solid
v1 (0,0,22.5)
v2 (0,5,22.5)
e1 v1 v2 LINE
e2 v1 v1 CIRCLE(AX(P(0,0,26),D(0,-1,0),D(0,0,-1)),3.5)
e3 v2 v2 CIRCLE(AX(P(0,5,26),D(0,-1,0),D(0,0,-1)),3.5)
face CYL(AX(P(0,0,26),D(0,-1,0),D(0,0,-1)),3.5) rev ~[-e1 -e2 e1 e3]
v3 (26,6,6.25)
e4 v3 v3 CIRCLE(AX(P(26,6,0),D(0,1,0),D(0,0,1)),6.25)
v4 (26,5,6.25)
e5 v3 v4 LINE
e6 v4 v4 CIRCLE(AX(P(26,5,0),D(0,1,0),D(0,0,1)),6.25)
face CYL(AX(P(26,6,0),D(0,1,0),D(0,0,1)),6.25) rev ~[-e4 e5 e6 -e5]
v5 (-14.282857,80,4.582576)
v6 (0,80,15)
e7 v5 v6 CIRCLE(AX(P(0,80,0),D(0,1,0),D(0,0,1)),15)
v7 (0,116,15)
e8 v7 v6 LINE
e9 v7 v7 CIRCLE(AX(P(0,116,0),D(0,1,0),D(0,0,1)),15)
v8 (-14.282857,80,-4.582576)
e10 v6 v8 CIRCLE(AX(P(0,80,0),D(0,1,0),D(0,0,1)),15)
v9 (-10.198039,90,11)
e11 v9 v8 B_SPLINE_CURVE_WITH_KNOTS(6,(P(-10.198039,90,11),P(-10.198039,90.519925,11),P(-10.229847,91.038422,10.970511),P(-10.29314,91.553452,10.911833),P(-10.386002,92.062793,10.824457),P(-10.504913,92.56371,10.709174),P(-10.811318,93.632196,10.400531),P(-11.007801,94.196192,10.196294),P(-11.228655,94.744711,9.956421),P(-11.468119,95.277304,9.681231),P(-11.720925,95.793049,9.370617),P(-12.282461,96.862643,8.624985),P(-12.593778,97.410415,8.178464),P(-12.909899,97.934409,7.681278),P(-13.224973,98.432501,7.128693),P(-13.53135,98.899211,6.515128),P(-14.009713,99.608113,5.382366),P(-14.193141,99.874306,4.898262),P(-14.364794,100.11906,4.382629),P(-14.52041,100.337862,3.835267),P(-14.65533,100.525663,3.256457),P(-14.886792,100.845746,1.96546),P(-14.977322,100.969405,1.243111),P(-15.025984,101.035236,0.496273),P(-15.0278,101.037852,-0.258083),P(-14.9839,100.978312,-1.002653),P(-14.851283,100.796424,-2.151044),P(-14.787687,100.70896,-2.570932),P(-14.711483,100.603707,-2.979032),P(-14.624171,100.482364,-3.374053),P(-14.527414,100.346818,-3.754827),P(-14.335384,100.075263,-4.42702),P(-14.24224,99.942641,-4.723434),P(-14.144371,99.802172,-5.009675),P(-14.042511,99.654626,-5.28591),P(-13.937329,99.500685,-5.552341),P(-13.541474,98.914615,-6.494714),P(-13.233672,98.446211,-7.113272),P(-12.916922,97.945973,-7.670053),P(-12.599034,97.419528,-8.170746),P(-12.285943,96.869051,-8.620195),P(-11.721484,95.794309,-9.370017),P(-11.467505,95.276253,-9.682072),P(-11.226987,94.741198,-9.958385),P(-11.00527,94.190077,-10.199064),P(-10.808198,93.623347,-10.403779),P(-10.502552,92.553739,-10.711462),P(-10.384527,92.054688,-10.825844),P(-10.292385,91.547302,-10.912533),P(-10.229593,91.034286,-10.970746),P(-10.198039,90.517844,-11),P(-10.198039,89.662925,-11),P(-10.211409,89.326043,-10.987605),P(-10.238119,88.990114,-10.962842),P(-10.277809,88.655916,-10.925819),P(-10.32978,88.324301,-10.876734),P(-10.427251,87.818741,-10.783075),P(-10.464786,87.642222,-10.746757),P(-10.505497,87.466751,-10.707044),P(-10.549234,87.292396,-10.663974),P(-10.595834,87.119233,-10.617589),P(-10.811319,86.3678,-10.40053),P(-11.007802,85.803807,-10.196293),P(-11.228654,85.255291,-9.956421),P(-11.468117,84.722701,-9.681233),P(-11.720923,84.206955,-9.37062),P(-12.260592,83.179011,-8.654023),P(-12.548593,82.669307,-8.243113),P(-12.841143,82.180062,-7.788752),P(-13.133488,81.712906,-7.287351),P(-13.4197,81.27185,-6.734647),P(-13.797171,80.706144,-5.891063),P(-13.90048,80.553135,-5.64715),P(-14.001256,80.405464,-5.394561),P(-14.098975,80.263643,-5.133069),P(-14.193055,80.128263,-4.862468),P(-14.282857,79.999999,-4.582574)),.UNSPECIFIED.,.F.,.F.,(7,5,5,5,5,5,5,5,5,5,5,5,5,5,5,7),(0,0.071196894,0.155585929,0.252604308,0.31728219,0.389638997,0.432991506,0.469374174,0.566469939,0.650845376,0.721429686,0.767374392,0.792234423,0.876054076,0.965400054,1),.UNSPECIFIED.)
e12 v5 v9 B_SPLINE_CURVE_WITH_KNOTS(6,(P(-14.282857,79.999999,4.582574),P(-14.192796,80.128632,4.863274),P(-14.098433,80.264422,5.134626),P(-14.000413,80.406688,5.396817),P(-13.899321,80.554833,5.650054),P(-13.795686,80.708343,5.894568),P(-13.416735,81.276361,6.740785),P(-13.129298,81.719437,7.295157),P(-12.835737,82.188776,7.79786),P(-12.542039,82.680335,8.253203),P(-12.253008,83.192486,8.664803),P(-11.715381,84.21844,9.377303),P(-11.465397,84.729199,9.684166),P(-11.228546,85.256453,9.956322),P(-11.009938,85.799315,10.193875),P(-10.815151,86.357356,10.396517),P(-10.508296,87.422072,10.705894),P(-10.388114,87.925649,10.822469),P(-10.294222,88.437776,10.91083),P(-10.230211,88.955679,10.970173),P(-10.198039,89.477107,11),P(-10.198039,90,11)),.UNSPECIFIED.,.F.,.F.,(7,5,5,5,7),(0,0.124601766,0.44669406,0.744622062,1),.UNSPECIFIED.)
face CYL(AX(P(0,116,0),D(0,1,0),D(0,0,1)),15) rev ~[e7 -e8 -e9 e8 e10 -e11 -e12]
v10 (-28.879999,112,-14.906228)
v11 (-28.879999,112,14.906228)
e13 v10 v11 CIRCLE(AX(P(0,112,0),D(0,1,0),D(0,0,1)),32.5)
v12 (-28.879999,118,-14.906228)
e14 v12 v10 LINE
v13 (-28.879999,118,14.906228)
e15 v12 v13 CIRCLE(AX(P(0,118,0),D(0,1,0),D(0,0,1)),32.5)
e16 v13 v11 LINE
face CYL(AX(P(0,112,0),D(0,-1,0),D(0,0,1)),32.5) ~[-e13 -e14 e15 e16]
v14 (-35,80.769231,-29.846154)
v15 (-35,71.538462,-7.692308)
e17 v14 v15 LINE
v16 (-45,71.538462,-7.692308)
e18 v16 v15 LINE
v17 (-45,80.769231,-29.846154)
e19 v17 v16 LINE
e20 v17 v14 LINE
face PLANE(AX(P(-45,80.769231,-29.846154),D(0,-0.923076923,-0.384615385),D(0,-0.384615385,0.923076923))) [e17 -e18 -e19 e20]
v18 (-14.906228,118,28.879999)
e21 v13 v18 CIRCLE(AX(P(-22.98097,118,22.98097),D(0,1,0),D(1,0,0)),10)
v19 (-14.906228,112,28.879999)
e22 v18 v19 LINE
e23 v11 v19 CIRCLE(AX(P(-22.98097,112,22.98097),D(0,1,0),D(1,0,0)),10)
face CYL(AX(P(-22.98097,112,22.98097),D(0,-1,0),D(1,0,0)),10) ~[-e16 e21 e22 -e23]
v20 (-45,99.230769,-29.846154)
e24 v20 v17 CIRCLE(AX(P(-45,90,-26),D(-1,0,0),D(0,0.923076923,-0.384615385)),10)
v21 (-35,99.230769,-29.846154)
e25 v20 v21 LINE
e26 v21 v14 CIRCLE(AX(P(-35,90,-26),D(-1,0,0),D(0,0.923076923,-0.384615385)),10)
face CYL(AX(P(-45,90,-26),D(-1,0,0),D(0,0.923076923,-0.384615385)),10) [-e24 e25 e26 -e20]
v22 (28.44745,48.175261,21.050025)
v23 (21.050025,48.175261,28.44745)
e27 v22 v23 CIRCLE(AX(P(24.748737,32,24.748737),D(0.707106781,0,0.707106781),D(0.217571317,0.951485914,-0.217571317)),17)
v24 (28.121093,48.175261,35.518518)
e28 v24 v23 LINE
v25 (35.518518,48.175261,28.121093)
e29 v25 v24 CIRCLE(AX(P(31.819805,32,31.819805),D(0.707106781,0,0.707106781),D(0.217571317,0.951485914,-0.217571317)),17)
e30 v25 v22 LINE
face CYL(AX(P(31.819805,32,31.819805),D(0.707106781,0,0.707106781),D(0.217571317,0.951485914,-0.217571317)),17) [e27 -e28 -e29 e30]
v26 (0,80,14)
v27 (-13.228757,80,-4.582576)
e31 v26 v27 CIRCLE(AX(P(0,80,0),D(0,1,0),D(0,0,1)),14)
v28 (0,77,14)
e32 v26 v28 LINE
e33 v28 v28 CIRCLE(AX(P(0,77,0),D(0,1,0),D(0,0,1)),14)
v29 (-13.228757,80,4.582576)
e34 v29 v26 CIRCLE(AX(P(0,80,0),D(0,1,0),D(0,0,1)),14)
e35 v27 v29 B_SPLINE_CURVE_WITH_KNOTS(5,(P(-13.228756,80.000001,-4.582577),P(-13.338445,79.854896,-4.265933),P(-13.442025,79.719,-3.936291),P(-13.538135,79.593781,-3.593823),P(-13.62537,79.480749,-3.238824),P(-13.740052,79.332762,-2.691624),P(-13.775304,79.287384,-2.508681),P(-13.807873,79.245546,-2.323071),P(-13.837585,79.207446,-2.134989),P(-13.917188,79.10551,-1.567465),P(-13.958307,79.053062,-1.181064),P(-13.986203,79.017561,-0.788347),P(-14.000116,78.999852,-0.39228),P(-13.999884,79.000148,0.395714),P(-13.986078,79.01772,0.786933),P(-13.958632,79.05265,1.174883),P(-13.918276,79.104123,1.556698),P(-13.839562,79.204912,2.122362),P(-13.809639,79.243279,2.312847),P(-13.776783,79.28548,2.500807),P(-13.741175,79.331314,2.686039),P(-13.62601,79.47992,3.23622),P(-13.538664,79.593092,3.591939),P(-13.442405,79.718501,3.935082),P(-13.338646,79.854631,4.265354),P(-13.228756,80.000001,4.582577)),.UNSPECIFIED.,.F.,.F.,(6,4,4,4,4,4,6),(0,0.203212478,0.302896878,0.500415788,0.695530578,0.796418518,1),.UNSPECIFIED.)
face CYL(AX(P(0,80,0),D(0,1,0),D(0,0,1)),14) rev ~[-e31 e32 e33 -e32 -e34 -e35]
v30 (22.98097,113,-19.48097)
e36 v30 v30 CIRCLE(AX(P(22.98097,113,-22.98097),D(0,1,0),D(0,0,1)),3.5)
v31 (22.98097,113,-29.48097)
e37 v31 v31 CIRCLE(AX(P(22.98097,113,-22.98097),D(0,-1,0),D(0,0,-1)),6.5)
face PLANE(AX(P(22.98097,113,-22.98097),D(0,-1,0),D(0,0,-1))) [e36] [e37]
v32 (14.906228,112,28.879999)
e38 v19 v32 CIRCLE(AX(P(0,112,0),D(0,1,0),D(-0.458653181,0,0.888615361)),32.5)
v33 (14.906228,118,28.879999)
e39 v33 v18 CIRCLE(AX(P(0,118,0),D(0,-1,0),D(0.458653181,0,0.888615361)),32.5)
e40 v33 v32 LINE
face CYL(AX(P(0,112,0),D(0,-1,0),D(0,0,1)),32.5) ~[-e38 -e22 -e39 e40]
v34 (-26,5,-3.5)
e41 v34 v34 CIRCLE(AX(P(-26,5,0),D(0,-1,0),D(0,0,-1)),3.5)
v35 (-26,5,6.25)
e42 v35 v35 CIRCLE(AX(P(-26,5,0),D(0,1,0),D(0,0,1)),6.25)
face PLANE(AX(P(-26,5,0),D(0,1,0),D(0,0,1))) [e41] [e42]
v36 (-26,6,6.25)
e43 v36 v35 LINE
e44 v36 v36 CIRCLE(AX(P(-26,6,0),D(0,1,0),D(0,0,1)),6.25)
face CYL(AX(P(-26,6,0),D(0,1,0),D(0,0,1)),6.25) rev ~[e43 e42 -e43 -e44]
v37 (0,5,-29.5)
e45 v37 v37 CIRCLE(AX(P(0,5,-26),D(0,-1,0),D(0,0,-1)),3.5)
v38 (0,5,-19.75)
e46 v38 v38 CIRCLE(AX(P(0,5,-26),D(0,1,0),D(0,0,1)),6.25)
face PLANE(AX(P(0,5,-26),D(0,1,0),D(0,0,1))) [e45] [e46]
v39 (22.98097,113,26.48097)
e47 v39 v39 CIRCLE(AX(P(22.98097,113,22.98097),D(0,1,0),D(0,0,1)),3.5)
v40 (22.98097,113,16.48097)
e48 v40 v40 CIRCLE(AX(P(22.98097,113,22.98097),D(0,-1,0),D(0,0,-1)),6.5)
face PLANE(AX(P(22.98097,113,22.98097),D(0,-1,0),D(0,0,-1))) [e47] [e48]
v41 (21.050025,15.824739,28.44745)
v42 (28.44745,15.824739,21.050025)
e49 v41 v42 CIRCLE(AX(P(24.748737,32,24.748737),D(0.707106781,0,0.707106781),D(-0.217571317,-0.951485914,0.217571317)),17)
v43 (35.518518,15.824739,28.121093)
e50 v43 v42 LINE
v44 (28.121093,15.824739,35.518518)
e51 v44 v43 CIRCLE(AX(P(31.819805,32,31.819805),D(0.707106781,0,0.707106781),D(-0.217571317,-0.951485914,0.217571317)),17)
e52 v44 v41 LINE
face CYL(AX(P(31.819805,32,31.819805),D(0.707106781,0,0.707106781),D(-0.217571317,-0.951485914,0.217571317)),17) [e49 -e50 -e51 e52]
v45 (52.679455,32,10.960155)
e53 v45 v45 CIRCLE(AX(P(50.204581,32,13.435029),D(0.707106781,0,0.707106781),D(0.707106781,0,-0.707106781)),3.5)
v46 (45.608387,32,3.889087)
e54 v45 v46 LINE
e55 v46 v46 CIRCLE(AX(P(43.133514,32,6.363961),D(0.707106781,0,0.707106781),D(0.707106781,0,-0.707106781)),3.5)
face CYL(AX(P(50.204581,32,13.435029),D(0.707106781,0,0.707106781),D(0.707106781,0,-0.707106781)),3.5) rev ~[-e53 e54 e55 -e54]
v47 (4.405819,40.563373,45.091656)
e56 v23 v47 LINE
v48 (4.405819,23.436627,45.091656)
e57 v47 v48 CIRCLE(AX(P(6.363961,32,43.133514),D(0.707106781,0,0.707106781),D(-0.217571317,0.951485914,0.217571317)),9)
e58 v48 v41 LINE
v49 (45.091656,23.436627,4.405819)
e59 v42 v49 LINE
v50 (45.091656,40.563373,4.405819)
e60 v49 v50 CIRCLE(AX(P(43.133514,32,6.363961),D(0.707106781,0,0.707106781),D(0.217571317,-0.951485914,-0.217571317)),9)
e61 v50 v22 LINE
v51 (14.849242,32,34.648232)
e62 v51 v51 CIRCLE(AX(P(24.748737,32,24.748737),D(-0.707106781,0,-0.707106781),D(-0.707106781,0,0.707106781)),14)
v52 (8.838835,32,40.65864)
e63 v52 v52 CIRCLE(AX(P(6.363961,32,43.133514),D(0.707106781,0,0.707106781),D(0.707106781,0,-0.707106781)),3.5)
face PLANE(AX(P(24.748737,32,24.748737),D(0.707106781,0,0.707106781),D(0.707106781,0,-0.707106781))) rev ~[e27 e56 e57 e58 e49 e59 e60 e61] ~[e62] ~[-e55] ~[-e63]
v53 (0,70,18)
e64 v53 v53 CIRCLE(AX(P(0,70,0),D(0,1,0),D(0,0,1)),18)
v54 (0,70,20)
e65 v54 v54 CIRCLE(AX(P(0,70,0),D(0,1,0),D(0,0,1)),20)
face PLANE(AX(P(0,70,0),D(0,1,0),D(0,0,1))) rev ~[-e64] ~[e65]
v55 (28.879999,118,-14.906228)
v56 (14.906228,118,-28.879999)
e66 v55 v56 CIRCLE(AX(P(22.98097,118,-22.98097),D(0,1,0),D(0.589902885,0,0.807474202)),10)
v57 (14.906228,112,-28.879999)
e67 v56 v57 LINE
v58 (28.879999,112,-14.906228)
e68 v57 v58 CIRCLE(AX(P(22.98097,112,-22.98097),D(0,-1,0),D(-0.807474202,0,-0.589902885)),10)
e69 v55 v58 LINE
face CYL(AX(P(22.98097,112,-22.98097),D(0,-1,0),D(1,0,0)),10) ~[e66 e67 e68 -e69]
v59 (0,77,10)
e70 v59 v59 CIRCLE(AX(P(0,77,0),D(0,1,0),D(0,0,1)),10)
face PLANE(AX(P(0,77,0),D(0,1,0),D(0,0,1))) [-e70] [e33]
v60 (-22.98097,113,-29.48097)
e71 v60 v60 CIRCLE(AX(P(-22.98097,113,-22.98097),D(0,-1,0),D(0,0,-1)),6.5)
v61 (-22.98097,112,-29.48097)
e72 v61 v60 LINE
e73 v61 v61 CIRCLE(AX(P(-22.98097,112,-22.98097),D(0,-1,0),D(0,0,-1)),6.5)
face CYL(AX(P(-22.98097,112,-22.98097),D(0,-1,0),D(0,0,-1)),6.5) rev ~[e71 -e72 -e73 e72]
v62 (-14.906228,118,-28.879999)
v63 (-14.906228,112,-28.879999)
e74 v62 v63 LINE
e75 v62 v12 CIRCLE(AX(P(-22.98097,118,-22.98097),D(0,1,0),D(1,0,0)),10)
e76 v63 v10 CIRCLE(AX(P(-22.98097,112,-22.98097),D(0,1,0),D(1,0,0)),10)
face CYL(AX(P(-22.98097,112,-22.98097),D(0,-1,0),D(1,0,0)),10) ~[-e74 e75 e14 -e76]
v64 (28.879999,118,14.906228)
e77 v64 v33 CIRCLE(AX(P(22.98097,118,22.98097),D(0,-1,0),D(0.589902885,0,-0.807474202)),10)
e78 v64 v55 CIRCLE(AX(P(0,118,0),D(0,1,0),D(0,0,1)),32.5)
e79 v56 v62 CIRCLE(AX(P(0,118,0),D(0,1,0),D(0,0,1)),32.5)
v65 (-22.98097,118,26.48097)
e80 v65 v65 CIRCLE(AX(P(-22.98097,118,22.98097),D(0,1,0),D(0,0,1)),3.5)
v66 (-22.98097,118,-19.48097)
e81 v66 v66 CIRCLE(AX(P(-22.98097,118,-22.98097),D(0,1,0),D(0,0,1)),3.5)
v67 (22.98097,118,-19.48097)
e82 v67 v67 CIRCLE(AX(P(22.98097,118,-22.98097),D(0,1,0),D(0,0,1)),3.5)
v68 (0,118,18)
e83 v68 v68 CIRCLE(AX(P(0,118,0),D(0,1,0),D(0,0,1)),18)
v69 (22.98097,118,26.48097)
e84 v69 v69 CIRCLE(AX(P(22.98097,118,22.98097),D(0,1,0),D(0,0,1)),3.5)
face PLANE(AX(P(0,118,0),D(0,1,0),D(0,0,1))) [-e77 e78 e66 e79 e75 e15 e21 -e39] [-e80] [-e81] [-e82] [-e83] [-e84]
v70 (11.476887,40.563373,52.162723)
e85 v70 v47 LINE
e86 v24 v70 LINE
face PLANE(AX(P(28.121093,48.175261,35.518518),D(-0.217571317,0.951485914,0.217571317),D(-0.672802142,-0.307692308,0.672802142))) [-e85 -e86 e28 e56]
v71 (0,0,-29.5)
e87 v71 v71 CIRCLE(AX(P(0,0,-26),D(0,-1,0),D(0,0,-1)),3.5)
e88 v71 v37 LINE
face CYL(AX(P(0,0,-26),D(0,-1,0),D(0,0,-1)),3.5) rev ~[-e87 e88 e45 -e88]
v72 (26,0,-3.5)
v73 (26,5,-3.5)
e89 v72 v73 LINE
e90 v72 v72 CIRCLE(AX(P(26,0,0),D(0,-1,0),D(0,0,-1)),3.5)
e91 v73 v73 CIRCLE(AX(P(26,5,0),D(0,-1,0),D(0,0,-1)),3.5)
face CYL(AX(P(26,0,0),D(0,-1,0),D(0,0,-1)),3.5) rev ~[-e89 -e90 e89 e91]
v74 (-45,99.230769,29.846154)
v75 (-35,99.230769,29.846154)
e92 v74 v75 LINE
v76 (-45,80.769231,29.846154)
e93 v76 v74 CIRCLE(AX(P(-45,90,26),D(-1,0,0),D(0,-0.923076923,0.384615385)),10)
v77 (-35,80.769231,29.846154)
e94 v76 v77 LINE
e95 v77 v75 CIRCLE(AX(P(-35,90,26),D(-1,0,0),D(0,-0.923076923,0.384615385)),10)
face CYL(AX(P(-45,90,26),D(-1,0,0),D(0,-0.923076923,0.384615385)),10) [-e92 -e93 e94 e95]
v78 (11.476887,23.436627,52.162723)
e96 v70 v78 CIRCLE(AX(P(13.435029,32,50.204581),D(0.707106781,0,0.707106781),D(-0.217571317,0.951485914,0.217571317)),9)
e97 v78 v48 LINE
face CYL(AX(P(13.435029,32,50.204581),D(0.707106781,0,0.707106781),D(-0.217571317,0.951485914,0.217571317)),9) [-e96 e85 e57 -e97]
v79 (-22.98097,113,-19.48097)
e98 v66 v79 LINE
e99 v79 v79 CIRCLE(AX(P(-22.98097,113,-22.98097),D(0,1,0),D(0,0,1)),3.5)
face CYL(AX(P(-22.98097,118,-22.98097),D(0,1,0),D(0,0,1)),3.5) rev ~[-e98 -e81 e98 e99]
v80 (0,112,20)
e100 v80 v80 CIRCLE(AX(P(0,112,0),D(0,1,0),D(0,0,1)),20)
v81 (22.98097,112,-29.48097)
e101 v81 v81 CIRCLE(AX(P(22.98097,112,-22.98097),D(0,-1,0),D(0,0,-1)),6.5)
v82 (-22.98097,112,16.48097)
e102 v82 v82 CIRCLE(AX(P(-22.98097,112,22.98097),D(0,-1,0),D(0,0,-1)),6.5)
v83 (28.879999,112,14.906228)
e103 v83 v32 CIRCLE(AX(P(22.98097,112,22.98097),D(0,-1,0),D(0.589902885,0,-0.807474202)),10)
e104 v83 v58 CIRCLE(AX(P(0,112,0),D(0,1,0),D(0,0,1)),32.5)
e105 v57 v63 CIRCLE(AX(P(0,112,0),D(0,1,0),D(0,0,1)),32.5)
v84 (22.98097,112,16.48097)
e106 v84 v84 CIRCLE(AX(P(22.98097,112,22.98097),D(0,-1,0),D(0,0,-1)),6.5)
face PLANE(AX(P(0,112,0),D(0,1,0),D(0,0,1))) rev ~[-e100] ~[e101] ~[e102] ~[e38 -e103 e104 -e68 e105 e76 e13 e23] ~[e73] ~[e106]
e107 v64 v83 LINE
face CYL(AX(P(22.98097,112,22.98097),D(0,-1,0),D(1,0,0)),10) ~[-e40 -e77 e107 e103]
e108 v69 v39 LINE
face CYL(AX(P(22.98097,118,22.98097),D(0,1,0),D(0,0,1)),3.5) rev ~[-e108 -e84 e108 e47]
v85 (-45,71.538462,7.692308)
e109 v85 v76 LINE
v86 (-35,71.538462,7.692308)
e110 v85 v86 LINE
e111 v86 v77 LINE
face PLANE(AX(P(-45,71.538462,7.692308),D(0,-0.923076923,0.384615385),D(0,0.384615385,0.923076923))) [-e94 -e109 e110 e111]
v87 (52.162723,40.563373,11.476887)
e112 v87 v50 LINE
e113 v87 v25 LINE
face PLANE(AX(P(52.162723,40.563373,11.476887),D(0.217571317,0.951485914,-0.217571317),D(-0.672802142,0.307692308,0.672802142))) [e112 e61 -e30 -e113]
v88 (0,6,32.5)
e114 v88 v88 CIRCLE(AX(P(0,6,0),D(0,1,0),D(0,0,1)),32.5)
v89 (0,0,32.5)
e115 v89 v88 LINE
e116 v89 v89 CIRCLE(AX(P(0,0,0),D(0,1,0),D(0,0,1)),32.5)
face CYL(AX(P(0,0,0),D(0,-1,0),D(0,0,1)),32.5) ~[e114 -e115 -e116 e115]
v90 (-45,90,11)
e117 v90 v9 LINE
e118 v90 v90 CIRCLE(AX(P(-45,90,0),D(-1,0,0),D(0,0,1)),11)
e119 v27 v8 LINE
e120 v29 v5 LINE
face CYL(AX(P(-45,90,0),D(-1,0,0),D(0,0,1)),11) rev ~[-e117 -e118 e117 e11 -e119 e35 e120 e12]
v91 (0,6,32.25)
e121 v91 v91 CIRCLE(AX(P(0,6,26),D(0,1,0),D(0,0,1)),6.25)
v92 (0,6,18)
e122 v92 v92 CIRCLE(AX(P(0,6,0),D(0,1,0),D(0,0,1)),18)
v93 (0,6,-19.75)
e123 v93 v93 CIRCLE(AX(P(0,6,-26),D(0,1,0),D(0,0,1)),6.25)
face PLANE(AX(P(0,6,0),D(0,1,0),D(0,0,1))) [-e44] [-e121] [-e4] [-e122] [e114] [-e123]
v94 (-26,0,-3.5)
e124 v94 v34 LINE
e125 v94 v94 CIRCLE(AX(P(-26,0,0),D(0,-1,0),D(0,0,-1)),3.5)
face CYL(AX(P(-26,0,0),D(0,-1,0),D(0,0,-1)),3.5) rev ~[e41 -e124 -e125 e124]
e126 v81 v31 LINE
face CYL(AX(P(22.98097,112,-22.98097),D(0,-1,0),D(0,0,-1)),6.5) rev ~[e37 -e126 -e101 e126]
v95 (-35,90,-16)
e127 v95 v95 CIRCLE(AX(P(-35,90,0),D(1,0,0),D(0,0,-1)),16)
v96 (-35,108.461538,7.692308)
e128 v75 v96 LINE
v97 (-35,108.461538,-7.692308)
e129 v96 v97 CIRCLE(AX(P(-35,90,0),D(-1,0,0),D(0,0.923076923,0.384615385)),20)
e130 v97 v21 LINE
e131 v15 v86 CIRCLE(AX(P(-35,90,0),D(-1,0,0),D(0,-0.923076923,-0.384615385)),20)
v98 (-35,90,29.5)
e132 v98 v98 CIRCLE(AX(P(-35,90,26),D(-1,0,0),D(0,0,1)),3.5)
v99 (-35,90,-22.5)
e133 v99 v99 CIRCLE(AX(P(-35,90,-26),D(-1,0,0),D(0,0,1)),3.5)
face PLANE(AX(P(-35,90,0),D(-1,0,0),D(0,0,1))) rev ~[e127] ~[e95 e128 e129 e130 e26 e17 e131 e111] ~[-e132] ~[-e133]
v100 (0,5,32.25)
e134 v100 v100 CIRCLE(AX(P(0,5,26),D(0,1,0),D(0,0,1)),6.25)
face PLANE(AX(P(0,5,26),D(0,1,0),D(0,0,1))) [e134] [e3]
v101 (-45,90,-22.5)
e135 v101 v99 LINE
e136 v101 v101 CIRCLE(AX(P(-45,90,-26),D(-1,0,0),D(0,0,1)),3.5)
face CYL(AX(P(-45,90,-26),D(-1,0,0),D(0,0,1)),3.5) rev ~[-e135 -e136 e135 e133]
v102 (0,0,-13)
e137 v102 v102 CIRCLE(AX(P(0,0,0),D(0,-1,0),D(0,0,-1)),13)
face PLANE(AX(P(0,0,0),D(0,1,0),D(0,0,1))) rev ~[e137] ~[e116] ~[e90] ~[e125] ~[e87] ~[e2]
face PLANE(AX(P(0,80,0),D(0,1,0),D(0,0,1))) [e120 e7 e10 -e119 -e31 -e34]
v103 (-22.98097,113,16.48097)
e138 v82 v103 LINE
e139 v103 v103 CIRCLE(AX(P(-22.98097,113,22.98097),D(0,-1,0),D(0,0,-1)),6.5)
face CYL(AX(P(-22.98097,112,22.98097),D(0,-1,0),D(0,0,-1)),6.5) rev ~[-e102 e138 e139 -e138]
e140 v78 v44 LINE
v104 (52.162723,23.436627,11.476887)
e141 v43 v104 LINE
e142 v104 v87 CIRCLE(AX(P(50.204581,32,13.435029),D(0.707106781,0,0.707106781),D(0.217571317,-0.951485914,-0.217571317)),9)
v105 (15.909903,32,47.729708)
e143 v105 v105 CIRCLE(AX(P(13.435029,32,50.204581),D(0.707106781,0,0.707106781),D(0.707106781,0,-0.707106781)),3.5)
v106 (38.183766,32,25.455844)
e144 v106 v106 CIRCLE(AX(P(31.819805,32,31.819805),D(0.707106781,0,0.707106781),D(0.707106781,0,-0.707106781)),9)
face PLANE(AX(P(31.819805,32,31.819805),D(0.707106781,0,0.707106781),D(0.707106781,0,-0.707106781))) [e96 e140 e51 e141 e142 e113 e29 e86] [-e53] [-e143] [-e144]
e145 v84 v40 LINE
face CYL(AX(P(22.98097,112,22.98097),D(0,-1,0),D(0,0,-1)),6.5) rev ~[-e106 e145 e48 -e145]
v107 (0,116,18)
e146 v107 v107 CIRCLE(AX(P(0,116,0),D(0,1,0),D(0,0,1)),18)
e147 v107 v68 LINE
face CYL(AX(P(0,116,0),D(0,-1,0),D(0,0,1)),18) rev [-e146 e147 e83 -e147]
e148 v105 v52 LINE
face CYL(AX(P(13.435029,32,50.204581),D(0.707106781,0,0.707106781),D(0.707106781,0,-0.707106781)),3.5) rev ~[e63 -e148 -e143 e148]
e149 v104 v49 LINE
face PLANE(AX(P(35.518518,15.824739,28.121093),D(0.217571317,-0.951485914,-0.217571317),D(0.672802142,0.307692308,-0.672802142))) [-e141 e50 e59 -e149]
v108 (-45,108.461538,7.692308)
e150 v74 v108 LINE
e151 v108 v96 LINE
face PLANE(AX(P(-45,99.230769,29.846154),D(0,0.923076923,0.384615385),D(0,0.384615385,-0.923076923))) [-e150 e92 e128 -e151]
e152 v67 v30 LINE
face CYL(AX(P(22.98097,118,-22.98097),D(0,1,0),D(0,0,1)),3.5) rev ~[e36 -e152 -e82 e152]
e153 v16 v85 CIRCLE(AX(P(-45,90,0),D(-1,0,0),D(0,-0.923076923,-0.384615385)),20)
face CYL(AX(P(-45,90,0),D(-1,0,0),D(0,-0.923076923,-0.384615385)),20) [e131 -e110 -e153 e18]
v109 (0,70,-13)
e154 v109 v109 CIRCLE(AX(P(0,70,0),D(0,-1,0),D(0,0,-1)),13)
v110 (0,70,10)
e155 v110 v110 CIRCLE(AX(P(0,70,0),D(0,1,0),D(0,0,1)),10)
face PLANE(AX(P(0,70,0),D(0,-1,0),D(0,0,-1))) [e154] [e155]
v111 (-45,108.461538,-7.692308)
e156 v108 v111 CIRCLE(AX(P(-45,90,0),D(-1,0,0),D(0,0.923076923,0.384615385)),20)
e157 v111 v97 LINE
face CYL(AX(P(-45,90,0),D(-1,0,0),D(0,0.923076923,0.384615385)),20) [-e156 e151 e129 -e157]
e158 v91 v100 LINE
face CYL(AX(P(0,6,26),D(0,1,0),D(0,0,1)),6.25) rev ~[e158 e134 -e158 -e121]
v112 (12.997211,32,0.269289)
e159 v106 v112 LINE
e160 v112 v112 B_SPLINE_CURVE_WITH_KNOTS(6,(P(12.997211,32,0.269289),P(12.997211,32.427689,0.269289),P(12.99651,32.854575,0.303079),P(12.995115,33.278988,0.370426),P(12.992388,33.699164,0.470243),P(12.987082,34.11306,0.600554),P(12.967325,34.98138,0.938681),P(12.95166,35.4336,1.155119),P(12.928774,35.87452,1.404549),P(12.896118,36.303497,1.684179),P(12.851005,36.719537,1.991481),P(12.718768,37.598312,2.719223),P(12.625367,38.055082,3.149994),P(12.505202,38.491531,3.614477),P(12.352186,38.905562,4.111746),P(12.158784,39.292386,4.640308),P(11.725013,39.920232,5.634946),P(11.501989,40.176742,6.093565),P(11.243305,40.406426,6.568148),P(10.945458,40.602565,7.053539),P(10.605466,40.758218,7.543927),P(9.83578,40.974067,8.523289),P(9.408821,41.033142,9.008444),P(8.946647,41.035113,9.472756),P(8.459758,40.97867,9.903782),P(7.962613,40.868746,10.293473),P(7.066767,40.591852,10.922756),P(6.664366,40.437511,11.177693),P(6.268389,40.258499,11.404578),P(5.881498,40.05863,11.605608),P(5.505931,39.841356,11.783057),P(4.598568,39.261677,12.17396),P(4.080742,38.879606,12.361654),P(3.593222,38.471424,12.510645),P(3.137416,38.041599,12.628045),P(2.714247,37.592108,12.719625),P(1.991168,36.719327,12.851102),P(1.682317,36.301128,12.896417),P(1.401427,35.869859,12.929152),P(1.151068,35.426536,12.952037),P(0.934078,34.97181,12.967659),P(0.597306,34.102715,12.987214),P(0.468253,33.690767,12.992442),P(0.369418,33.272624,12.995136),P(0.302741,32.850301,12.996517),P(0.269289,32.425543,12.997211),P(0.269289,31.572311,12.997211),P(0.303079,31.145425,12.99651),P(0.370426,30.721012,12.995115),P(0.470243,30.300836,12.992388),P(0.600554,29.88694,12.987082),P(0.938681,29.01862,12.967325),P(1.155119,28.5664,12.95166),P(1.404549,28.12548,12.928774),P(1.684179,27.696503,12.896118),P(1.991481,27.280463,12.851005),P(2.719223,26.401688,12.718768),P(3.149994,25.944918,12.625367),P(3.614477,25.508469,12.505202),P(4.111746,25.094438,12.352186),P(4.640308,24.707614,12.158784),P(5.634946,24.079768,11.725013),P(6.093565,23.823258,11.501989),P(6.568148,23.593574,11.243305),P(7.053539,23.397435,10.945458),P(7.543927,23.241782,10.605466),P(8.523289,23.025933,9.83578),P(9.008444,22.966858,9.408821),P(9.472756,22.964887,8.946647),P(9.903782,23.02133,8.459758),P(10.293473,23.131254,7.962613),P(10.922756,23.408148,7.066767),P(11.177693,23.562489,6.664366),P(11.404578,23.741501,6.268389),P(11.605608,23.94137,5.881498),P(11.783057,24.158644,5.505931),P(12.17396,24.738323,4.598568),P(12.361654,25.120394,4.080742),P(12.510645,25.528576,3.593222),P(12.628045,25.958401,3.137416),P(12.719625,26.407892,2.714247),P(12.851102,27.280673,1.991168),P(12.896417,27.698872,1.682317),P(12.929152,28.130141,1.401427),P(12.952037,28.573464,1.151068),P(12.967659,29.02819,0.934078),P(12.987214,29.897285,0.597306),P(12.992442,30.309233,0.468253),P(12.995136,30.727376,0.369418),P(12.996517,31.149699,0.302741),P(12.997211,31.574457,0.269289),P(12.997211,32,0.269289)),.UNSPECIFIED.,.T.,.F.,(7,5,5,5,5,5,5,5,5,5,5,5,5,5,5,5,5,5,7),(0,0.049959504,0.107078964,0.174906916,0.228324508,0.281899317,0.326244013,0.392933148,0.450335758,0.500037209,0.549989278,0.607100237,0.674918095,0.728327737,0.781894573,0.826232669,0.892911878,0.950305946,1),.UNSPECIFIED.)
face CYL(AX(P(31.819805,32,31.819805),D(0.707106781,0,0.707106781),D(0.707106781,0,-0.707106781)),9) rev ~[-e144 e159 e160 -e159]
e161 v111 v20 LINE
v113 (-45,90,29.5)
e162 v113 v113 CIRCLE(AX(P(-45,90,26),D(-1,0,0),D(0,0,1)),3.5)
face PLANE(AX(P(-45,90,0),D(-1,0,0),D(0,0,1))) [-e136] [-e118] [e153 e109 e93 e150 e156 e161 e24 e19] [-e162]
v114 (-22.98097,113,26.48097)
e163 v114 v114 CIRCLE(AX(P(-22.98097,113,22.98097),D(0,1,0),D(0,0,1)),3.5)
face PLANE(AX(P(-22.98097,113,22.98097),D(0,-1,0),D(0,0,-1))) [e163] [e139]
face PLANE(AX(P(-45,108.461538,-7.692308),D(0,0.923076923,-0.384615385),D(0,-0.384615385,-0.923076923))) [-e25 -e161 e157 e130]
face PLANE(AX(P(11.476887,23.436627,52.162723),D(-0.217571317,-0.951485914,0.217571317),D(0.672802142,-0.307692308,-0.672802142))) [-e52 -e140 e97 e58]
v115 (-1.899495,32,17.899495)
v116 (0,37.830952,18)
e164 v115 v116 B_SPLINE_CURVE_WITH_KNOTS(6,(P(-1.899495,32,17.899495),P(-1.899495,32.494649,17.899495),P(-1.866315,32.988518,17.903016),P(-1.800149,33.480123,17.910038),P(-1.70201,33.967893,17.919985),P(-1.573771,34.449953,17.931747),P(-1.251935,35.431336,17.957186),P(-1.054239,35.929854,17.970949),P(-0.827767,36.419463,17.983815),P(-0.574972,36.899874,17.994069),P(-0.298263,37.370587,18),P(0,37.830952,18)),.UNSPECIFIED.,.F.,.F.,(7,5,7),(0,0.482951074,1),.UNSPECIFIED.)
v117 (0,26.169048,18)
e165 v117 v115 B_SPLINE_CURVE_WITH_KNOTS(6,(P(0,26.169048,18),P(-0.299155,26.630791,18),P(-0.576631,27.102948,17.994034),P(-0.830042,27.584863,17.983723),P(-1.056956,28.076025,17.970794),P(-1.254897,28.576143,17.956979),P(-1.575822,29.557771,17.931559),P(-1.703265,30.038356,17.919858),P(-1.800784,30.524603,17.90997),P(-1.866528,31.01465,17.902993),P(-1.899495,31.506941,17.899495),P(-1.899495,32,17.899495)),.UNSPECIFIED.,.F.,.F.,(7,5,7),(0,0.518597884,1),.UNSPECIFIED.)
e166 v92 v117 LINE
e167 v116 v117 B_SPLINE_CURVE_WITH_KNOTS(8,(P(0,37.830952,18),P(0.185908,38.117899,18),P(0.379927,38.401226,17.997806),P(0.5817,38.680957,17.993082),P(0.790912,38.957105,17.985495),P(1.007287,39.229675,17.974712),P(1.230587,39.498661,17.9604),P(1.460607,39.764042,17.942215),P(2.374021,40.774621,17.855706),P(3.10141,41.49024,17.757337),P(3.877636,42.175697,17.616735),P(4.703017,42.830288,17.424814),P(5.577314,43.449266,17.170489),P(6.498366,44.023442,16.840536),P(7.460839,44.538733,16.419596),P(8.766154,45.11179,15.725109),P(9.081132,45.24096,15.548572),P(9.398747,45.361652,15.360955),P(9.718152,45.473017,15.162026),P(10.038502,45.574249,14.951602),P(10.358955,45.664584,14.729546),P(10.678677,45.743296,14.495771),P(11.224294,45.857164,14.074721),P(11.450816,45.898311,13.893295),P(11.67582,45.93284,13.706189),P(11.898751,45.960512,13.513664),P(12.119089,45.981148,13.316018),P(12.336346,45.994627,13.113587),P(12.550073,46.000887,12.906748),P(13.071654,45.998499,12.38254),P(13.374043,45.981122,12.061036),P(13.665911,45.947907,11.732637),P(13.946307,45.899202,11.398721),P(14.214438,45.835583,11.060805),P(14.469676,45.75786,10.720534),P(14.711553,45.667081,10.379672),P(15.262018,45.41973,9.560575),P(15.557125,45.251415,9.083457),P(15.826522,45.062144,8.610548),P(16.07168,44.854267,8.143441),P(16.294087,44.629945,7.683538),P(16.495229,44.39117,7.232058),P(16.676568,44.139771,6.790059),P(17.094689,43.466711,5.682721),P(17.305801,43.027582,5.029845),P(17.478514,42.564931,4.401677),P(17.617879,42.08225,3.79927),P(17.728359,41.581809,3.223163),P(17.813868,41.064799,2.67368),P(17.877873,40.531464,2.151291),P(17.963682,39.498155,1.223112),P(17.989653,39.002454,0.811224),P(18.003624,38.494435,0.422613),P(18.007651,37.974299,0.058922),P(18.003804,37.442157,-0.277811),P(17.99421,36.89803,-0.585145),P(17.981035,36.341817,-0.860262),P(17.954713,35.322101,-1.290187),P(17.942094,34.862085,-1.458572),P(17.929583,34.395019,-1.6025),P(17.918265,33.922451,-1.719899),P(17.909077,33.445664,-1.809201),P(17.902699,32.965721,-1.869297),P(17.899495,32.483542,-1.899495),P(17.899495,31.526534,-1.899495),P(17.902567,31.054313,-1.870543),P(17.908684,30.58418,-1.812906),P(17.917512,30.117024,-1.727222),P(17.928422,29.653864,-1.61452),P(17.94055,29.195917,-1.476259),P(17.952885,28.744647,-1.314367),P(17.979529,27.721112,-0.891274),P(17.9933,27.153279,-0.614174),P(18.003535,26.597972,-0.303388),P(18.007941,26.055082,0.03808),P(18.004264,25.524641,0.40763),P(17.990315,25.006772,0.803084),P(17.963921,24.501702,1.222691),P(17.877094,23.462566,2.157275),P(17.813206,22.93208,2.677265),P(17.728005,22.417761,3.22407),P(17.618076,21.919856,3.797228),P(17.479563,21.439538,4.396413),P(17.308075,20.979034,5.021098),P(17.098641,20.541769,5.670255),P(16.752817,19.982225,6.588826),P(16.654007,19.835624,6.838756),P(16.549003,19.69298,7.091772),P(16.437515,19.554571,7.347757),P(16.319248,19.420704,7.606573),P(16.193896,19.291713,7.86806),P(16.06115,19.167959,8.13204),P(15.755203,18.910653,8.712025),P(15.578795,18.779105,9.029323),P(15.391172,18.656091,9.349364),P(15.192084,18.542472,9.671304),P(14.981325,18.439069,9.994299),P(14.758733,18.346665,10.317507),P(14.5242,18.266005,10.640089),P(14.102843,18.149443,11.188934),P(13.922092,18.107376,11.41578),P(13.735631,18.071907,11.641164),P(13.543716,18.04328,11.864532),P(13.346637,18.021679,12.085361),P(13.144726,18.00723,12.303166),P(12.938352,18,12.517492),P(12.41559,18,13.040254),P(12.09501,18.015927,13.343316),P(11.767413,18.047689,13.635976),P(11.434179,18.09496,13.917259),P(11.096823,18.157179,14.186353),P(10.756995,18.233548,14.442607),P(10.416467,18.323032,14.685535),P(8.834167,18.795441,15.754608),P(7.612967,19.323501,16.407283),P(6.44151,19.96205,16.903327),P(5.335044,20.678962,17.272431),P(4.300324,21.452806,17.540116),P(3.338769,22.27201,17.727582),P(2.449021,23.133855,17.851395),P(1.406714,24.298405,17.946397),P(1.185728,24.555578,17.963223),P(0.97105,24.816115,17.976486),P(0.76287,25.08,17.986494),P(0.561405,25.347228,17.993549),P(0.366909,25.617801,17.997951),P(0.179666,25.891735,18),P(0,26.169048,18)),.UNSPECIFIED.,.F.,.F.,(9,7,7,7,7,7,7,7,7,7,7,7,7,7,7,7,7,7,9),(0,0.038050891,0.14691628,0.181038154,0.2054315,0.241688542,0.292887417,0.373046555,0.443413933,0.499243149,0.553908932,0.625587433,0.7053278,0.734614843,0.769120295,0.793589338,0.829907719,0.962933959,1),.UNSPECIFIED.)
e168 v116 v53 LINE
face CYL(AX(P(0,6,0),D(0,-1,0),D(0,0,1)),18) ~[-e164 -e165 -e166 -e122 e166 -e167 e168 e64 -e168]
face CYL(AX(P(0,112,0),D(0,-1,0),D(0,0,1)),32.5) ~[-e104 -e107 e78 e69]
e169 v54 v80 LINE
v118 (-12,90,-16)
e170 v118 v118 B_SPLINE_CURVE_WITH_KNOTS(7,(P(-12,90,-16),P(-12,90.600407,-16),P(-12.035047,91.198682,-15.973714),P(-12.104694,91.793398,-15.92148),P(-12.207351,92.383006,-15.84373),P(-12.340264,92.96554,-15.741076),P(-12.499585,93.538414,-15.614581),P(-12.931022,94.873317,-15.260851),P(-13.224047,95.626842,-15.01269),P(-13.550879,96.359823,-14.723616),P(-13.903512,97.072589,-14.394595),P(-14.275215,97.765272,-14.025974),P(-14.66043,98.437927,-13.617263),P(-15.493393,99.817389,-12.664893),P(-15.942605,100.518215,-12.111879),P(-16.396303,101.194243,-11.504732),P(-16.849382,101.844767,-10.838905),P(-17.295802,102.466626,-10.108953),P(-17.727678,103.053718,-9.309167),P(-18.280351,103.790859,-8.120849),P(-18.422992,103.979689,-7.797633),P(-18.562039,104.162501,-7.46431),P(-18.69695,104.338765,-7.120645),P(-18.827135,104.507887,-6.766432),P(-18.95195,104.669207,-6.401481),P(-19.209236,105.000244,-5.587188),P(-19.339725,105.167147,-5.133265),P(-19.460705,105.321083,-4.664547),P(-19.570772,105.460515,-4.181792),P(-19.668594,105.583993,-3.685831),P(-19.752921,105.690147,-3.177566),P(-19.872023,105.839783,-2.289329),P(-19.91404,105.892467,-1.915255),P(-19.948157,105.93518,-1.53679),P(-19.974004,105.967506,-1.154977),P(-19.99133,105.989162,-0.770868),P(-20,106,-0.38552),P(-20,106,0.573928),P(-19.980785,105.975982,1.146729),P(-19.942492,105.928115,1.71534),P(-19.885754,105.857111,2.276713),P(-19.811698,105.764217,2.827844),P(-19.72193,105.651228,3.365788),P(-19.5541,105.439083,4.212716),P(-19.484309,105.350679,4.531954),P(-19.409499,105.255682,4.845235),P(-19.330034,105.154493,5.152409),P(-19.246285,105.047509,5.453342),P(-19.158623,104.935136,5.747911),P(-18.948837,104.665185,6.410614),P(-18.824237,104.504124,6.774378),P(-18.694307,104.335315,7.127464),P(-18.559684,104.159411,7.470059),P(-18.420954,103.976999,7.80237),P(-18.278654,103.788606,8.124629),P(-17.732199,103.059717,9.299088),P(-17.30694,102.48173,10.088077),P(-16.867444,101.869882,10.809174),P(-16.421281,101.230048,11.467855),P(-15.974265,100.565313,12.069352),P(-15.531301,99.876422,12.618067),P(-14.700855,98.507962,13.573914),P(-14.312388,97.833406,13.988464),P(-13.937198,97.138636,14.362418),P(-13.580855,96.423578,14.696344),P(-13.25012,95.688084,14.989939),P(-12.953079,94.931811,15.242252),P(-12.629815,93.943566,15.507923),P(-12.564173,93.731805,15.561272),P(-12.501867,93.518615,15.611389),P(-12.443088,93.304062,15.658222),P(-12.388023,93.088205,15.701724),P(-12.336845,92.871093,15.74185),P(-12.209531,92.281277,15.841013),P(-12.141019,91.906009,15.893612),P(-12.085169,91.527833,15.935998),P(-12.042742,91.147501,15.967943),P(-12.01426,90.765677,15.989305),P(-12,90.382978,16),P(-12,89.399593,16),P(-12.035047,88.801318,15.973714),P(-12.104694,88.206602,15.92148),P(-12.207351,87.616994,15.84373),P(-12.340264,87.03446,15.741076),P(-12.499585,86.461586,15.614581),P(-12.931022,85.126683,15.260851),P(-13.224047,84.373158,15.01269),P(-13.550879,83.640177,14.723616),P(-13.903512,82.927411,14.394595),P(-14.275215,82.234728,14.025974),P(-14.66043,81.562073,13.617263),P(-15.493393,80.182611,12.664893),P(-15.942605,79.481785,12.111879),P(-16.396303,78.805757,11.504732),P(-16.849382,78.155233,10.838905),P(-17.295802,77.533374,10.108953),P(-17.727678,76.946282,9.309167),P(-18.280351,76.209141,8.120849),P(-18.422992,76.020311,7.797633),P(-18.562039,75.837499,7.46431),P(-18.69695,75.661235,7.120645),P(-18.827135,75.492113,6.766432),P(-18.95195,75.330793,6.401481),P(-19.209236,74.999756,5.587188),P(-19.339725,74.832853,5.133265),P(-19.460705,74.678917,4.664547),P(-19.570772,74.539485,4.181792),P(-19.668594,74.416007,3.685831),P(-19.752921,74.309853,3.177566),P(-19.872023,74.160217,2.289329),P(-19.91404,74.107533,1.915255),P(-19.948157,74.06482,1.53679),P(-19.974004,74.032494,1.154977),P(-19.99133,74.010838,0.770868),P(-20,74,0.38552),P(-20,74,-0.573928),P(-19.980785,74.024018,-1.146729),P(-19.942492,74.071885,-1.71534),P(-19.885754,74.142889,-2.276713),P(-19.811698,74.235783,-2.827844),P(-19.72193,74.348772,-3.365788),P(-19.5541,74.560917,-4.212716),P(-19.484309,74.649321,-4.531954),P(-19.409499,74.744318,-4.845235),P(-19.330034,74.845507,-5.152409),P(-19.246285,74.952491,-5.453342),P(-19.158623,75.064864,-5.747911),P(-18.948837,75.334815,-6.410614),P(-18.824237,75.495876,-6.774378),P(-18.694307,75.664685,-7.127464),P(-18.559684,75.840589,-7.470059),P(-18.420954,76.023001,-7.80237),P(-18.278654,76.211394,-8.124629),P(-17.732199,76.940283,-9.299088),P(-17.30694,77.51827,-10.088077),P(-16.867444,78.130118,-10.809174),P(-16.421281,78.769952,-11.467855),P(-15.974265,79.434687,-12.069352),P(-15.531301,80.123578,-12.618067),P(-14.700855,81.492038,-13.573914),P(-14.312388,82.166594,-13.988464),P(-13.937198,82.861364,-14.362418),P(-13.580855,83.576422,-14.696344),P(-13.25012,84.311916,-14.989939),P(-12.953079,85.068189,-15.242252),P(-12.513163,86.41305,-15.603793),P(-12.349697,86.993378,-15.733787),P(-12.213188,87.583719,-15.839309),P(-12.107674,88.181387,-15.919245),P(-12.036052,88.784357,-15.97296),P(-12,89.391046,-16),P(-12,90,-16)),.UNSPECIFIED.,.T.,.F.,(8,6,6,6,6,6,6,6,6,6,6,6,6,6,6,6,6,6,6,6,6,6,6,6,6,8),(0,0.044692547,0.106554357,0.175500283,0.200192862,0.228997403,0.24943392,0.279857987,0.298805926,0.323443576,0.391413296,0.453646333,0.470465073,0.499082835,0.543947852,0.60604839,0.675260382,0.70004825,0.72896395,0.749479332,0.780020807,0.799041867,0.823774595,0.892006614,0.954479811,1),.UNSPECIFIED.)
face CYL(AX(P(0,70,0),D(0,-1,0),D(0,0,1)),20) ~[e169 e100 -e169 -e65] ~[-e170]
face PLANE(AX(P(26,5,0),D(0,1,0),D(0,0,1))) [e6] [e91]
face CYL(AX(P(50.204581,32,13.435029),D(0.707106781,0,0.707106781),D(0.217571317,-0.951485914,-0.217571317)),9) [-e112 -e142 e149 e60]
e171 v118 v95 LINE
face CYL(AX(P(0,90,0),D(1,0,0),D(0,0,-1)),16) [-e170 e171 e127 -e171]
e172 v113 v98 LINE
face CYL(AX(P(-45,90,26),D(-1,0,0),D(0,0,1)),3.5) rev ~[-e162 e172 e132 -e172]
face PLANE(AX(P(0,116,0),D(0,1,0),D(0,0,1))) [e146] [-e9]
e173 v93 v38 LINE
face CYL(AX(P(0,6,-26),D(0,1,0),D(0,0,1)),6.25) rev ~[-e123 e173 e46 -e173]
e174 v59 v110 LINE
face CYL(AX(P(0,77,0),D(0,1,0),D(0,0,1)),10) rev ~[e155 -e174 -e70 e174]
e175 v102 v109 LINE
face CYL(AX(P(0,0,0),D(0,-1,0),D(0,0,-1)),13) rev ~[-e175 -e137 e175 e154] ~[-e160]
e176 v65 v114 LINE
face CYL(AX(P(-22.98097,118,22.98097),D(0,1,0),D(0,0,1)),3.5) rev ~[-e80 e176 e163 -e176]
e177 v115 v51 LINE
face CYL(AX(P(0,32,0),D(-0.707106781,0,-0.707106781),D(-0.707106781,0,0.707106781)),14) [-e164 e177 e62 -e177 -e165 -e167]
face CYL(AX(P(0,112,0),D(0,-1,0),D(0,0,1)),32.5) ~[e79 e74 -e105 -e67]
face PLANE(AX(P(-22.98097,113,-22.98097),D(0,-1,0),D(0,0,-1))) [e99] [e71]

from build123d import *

# Parameters (mm, degrees)
SKETCH1_R           = 32.5
BOSS_EXTRUDE1_DEPTH = 6
SKETCH2_R           = 18
BOSS_EXTRUDE2_DEPTH = 64
SKETCH3_R           = 20
BOSS_EXTRUDE3_DEPTH = 48
BOSS_EXTRUDE4_START = -6
SKETCH4_R           = 32.5
SKETCH4_R_2         = 10
SKETCH4_R_3         = 20
BOSS_EXTRUDE4_DEPTH = 6
SKETCH5_R           = 16
BOSS_EXTRUDE5_DEPTH = 45
BOSS_EXTRUDE6_DEPTH = 10
SKETCH8_R           = 14
BOSS_EXTRUDE7_DEPTH = 45
BOSS_EXTRUDE8_DEPTH = 10
SKETCH10_R          = 13
CUT_EXTRUDE1_DEPTH  = 70
SKETCH11_R          = 9
CUT_EXTRUDE2_DEPTH  = 45
SKETCH12_R          = 11
CUT_EXTRUDE3_DEPTH  = 45
CUT_EXTRUDE4_START  = -2
SKETCH13_R          = 18
CUT_EXTRUDE4_DEPTH  = 2
SKETCH14_R          = 15
CUT_EXTRUDE5_DEPTH  = 36
SKETCH15_R          = 14
CUT_EXTRUDE6_DEPTH  = 3
SKETCH16_R          = 3.5
CUT_EXTRUDE7_DEPTH  = 20
SKETCH17_R          = 6.5
CUT_EXTRUDE8_DEPTH  = 1
SKETCH18_R          = 3.5
CUT_EXTRUDE9_DEPTH  = 10
SKETCH19_R          = 3.5
CUT_EXTRUDE10_DEPTH = 10
SKETCH20_R          = 3.5
CUT_EXTRUDE11_DEPTH = 20
SKETCH21_R          = 6.25
CUT_EXTRUDE12_DEPTH = 1
SKETCH22_R          = 10
CUT_EXTRUDE13_DEPTH = 50


with BuildPart() as part:
    # Sketch1 → Boss-Extrude1 (new body)
    with BuildSketch(Plane(origin=(0, 0, 0), x_dir=(1, 0, 0), z_dir=(0, 1, 0))):
        with Locations(Location((0, 0, 0), (0, 0, 270))):
            Circle(SKETCH1_R)
    extrude(amount=BOSS_EXTRUDE1_DEPTH)

    # Sketch2 → Boss-Extrude2 (add)
    with BuildSketch(Plane(origin=(0, 6, 0), x_dir=(1, 0, 0), z_dir=(0, 1, 0))):
        with Locations(Location((0, 0, 0), (0, 0, 270))):
            Circle(SKETCH2_R)
    extrude(amount=BOSS_EXTRUDE2_DEPTH)

    # Sketch3 → Boss-Extrude3 (add)
    with BuildSketch(Plane(origin=(0, 70, 0), x_dir=(1, 0, 0), z_dir=(0, 1, 0))):
        with Locations(Location((0, 0, 0), (0, 0, 270))):
            Circle(SKETCH3_R)
    extrude(amount=BOSS_EXTRUDE3_DEPTH)

    # Sketch4 → Boss-Extrude4 (add)
    # profile 1 of 18: a face of its own
    with BuildSketch(Plane(origin=(0, 118, 0), x_dir=(1, 0, 0), z_dir=(0, 1, 0)).offset(BOSS_EXTRUDE4_START)):
        with Locations(Location((0, 0, 0), (0, 0, 270))):
            Circle(SKETCH4_R)
    # profile 2 of 18: a face of its own
    with BuildSketch(Plane(origin=(0, 118, 0), x_dir=(1, 0, 0), z_dir=(0, 1, 0)).offset(BOSS_EXTRUDE4_START)):
        with Locations((22.980970389, 22.980970389)):
            Circle(SKETCH4_R_2)
    # profile 3 of 18: a face of its own
    with BuildSketch(Plane(origin=(0, 118, 0), x_dir=(1, 0, 0), z_dir=(0, 1, 0)).offset(BOSS_EXTRUDE4_START)):
        with Locations(Location((0, 0, 0), (0, 0, 270))):
            Circle(SKETCH4_R)
    # profile 4 of 18: a face of its own
    with BuildSketch(Plane(origin=(0, 118, 0), x_dir=(1, 0, 0), z_dir=(0, 1, 0)).offset(BOSS_EXTRUDE4_START)):
        with Locations((22.980970389, 22.980970389)):
            Circle(SKETCH4_R_2)
    # profile 5 of 18: a face of its own
    with BuildSketch(Plane(origin=(0, 118, 0), x_dir=(1, 0, 0), z_dir=(0, 1, 0)).offset(BOSS_EXTRUDE4_START)):
        with Locations((-22.980970389, 22.980970389)):
            Circle(SKETCH4_R_2)
    # profile 6 of 18: a face of its own
    with BuildSketch(Plane(origin=(0, 118, 0), x_dir=(1, 0, 0), z_dir=(0, 1, 0)).offset(BOSS_EXTRUDE4_START)):
        with Locations(Location((0, 0, 0), (0, 0, 270))):
            Circle(SKETCH4_R)
        with Locations(Location((0, 0, 0), (0, 0, 270))):
            Circle(SKETCH4_R_3, mode=Mode.SUBTRACT)
    # profile 7 of 18: a face of its own
    with BuildSketch(Plane(origin=(0, 118, 0), x_dir=(1, 0, 0), z_dir=(0, 1, 0)).offset(BOSS_EXTRUDE4_START)):
        with Locations((-22.980970389, -22.980970389)):
            Circle(SKETCH4_R_2)
    # profile 8 of 18: a face of its own
    with BuildSketch(Plane(origin=(0, 118, 0), x_dir=(1, 0, 0), z_dir=(0, 1, 0)).offset(BOSS_EXTRUDE4_START)):
        with Locations((22.980970389, -22.980970389)):
            Circle(SKETCH4_R_2)
    # profile 9 of 18: a face of its own
    with BuildSketch(Plane(origin=(0, 118, 0), x_dir=(1, 0, 0), z_dir=(0, 1, 0)).offset(BOSS_EXTRUDE4_START)):
        with Locations((22.980970389, 22.980970389)):
            Circle(SKETCH4_R_2)
    # profile 10 of 18: a face of its own
    with BuildSketch(Plane(origin=(0, 118, 0), x_dir=(1, 0, 0), z_dir=(0, 1, 0)).offset(BOSS_EXTRUDE4_START)):
        with Locations(Location((0, 0, 0), (0, 0, 270))):
            Circle(SKETCH4_R_3)
    # profile 11 of 18: a face of its own
    with BuildSketch(Plane(origin=(0, 118, 0), x_dir=(1, 0, 0), z_dir=(0, 1, 0)).offset(BOSS_EXTRUDE4_START)):
        with Locations(Location((0, 0, 0), (0, 0, 270))):
            Circle(SKETCH4_R)
    # profile 12 of 18: a face of its own
    with BuildSketch(Plane(origin=(0, 118, 0), x_dir=(1, 0, 0), z_dir=(0, 1, 0)).offset(BOSS_EXTRUDE4_START)):
        with Locations((22.980970389, -22.980970389)):
            Circle(SKETCH4_R_2)
    # profile 13 of 18: a face of its own
    with BuildSketch(Plane(origin=(0, 118, 0), x_dir=(1, 0, 0), z_dir=(0, 1, 0)).offset(BOSS_EXTRUDE4_START)):
        with Locations(Location((0, 0, 0), (0, 0, 270))):
            Circle(SKETCH4_R)
    # profile 14 of 18: a face of its own
    with BuildSketch(Plane(origin=(0, 118, 0), x_dir=(1, 0, 0), z_dir=(0, 1, 0)).offset(BOSS_EXTRUDE4_START)):
        with Locations((22.980970389, -22.980970389)):
            Circle(SKETCH4_R_2)
    # profile 15 of 18: a face of its own
    with BuildSketch(Plane(origin=(0, 118, 0), x_dir=(1, 0, 0), z_dir=(0, 1, 0)).offset(BOSS_EXTRUDE4_START)):
        with Locations(Location((0, 0, 0), (0, 0, 270))):
            Circle(SKETCH4_R)
    # profile 16 of 18: a face of its own
    with BuildSketch(Plane(origin=(0, 118, 0), x_dir=(1, 0, 0), z_dir=(0, 1, 0)).offset(BOSS_EXTRUDE4_START)):
        with Locations((-22.980970389, -22.980970389)):
            Circle(SKETCH4_R_2)
    # profile 17 of 18: a face of its own
    with BuildSketch(Plane(origin=(0, 118, 0), x_dir=(1, 0, 0), z_dir=(0, 1, 0)).offset(BOSS_EXTRUDE4_START)):
        with Locations(Location((0, 0, 0), (0, 0, 270))):
            Circle(SKETCH4_R)
    # profile 18 of 18: a face of its own
    with BuildSketch(Plane(origin=(0, 118, 0), x_dir=(1, 0, 0), z_dir=(0, 1, 0)).offset(BOSS_EXTRUDE4_START)):
        with Locations((-22.980970389, -22.980970389)):
            Circle(SKETCH4_R_2)
    extrude(amount=BOSS_EXTRUDE4_DEPTH)

    # Sketch5 → Boss-Extrude5 (add)
    with BuildSketch(Plane(origin=(0, 0, 0), x_dir=(0, 0, -1), z_dir=(1, 0, 0))):
        with Locations((0, 90)):
            Circle(SKETCH5_R)
    extrude(amount=-BOSS_EXTRUDE5_DEPTH)

    # Sketch6 → Boss-Extrude6 (add)
    with BuildSketch(Plane.ZY.offset(45)):
        with BuildLine():
            Line((7.692307692, 71.538461538), (29.846153846, 80.769230769))
            ThreePointArc((29.846153846, 80.769230769), (36, 90), (29.846153846, 99.230769231))
            Line((29.846153846, 99.230769231), (7.692307692, 108.461538462))
            ThreePointArc((7.692307692, 108.461538462), (0, 110), (-7.692307692, 108.461538462))
            Line((-7.692307692, 108.461538462), (-29.846153846, 99.230769231))
            ThreePointArc((-29.846153846, 99.230769231), (-36, 90), (-29.846153846, 80.769230769))
            Line((-29.846153846, 80.769230769), (-7.692307692, 71.538461538))
            ThreePointArc((-7.692307692, 71.538461538), (0, 70), (7.692307692, 71.538461538))
        make_face()
    extrude(amount=-BOSS_EXTRUDE6_DEPTH)

    # Sketch8 → Boss-Extrude7 (add)
    with BuildSketch(Plane(origin=(0, 0, 0), x_dir=(0, -1, 0), z_dir=(-0.7071067811865464, 0, -0.7071067811865488))):
        with Locations(Location((-32, 0, 0), (0, 0, 90))):
            Circle(SKETCH8_R)
    extrude(amount=-BOSS_EXTRUDE7_DEPTH)

    # Sketch9 → Boss-Extrude8 (add)
    with BuildSketch(Plane(origin=(31.819805153, 0, 31.819805153), x_dir=(0.7071067811865487, 0, -0.7071067811865465), z_dir=(0.7071067811865465, 0, 0.7071067811865487))):
        with BuildLine():
            Line((5.230769231, 15.824739469), (28.769230769, 23.436626778))
            ThreePointArc((28.769230769, 23.436626778), (35, 32), (28.769230769, 40.563373222))
            Line((28.769230769, 40.563373222), (5.230769231, 48.175260531))
            ThreePointArc((5.230769231, 48.175260531), (0, 49), (-5.230769231, 48.175260531))
            Line((-5.230769231, 48.175260531), (-28.769230769, 40.563373222))
            ThreePointArc((-28.769230769, 40.563373222), (-35, 32), (-28.769230769, 23.436626778))
            Line((-28.769230769, 23.436626778), (-5.230769231, 15.824739469))
            ThreePointArc((-5.230769231, 15.824739469), (0, 15), (5.230769231, 15.824739469))
        make_face()
    extrude(amount=-BOSS_EXTRUDE8_DEPTH)

    # Sketch10 → Cut-Extrude1 (cut)
    with BuildSketch(Plane.XZ):
        with Locations(Location((0, 0, 0), (0, 0, 270))):
            Circle(SKETCH10_R)
    extrude(amount=-CUT_EXTRUDE1_DEPTH, mode=Mode.SUBTRACT)

    # Sketch11 → Cut-Extrude2 (cut)
    with BuildSketch(Plane(origin=(31.819805153, 0, 31.819805153), x_dir=(0.7071067811865487, 0, -0.7071067811865465), z_dir=(0.7071067811865465, 0, 0.7071067811865487))):
        with Locations((0, 32)):
            Circle(SKETCH11_R)
    extrude(amount=-CUT_EXTRUDE2_DEPTH, mode=Mode.SUBTRACT)

    # Sketch12 → Cut-Extrude3 (cut)
    with BuildSketch(Plane.ZY.offset(45)):
        with Locations((0, 90)):
            Circle(SKETCH12_R)
    extrude(amount=-CUT_EXTRUDE3_DEPTH, mode=Mode.SUBTRACT)

    # Sketch13 → Cut-Extrude4 (cut)
    with BuildSketch(Plane(origin=(0, 118, 0), x_dir=(1, 0, 0), z_dir=(0, 1, 0)).offset(CUT_EXTRUDE4_START)):
        with Locations(Location((0, 0, 0), (0, 0, 270))):
            Circle(SKETCH13_R)
    extrude(amount=CUT_EXTRUDE4_DEPTH, mode=Mode.SUBTRACT)

    # Sketch14 → Cut-Extrude5 (cut)
    with BuildSketch(Plane(origin=(0, 116, 0), x_dir=(1, 0, 0), z_dir=(0, 1, 0))):
        with Locations(Location((0, 0, 0), (0, 0, 270))):
            Circle(SKETCH14_R)
    extrude(amount=-CUT_EXTRUDE5_DEPTH, mode=Mode.SUBTRACT)

    # Sketch15 → Cut-Extrude6 (cut)
    with BuildSketch(Plane(origin=(0, 80, 0), x_dir=(1, 0, 0), z_dir=(0, 1, 0))):
        with Locations(Location((0, 0, 0), (0, 0, 270))):
            Circle(SKETCH15_R)
    extrude(amount=-CUT_EXTRUDE6_DEPTH, mode=Mode.SUBTRACT)

    # Sketch16 → Cut-Extrude7 (cut)
    with BuildSketch(Plane(origin=(0, 118, 0), x_dir=(1, 0, 0), z_dir=(0, 1, 0))):
        with Locations(Location((22.980970389, 22.980970389, 0), (0, 0, 270))):
            Circle(SKETCH16_R)
        with Locations(Location((22.980970389, -22.980970389, 0), (0, 0, 270))):
            Circle(SKETCH16_R)
        with Locations(Location((-22.980970389, -22.980970389, 0), (0, 0, 270))):
            Circle(SKETCH16_R)
        with Locations(Location((-22.980970389, 22.980970389, 0), (0, 0, 270))):
            Circle(SKETCH16_R)
    extrude(amount=-CUT_EXTRUDE7_DEPTH, mode=Mode.SUBTRACT)

    # Sketch17 → Cut-Extrude8 (cut)
    with BuildSketch(Plane.XZ.offset(-112)):
        with Locations(Location((22.980970389, 22.980970389, 0), (0, 0, 270))):
            Circle(SKETCH17_R)
        with Locations(Location((22.980970389, -22.980970389, 0), (0, 0, 270))):
            Circle(SKETCH17_R)
        with Locations(Location((-22.980970389, -22.980970389, 0), (0, 0, 270))):
            Circle(SKETCH17_R)
        with Locations(Location((-22.980970389, 22.980970389, 0), (0, 0, 270))):
            Circle(SKETCH17_R)
    extrude(amount=-CUT_EXTRUDE8_DEPTH, mode=Mode.SUBTRACT)

    # Sketch18 → Cut-Extrude9 (cut)
    with BuildSketch(Plane(origin=(31.819805153, 0, 31.819805153), x_dir=(0.7071067811865487, 0, -0.7071067811865465), z_dir=(0.7071067811865465, 0, 0.7071067811865487))):
        with Locations((-26, 32)):
            Circle(SKETCH18_R)
        with Locations((26, 32)):
            Circle(SKETCH18_R)
    extrude(amount=-CUT_EXTRUDE9_DEPTH, mode=Mode.SUBTRACT)

    # Sketch19 → Cut-Extrude10 (cut)
    with BuildSketch(Plane.ZY.offset(45)):
        with Locations((26, 90)):
            Circle(SKETCH19_R)
        with Locations((-26, 90)):
            Circle(SKETCH19_R)
    extrude(amount=-CUT_EXTRUDE10_DEPTH, mode=Mode.SUBTRACT)

    # Sketch20 → Cut-Extrude11 (cut)
    with BuildSketch(Plane.XZ):
        with Locations(Location((0, -26, 0), (0, 0, 270))):
            Circle(SKETCH20_R)
        with Locations(Location((-26, 0, 0), (0, 0, 270))):
            Circle(SKETCH20_R)
        with Locations(Location((0, 26, 0), (0, 0, 270))):
            Circle(SKETCH20_R)
        with Locations(Location((26, 0, 0), (0, 0, 270))):
            Circle(SKETCH20_R)
    extrude(amount=-CUT_EXTRUDE11_DEPTH, mode=Mode.SUBTRACT)

    # Sketch21 → Cut-Extrude12 (cut)
    with BuildSketch(Plane(origin=(0, 6, 0), x_dir=(1, 0, 0), z_dir=(0, 1, 0))):
        with Locations(Location((-26, 0, 0), (0, 0, 270))):
            Circle(SKETCH21_R)
        with Locations(Location((0, 26, 0), (0, 0, 270))):
            Circle(SKETCH21_R)
        with Locations(Location((26, 0, 0), (0, 0, 270))):
            Circle(SKETCH21_R)
        with Locations(Location((0, -26, 0), (0, 0, 270))):
            Circle(SKETCH21_R)
    extrude(amount=-CUT_EXTRUDE12_DEPTH, mode=Mode.SUBTRACT)

    # Sketch22 → Cut-Extrude13 (cut)
    with BuildSketch(Plane(origin=(0, 77, 0), x_dir=(1, 0, 0), z_dir=(0, 1, 0))):
        with Locations(Location((0, 0, 0), (0, 0, 270))):
            Circle(SKETCH22_R)
    extrude(amount=-CUT_EXTRUDE13_DEPTH, mode=Mode.SUBTRACT)


solid = part.part
